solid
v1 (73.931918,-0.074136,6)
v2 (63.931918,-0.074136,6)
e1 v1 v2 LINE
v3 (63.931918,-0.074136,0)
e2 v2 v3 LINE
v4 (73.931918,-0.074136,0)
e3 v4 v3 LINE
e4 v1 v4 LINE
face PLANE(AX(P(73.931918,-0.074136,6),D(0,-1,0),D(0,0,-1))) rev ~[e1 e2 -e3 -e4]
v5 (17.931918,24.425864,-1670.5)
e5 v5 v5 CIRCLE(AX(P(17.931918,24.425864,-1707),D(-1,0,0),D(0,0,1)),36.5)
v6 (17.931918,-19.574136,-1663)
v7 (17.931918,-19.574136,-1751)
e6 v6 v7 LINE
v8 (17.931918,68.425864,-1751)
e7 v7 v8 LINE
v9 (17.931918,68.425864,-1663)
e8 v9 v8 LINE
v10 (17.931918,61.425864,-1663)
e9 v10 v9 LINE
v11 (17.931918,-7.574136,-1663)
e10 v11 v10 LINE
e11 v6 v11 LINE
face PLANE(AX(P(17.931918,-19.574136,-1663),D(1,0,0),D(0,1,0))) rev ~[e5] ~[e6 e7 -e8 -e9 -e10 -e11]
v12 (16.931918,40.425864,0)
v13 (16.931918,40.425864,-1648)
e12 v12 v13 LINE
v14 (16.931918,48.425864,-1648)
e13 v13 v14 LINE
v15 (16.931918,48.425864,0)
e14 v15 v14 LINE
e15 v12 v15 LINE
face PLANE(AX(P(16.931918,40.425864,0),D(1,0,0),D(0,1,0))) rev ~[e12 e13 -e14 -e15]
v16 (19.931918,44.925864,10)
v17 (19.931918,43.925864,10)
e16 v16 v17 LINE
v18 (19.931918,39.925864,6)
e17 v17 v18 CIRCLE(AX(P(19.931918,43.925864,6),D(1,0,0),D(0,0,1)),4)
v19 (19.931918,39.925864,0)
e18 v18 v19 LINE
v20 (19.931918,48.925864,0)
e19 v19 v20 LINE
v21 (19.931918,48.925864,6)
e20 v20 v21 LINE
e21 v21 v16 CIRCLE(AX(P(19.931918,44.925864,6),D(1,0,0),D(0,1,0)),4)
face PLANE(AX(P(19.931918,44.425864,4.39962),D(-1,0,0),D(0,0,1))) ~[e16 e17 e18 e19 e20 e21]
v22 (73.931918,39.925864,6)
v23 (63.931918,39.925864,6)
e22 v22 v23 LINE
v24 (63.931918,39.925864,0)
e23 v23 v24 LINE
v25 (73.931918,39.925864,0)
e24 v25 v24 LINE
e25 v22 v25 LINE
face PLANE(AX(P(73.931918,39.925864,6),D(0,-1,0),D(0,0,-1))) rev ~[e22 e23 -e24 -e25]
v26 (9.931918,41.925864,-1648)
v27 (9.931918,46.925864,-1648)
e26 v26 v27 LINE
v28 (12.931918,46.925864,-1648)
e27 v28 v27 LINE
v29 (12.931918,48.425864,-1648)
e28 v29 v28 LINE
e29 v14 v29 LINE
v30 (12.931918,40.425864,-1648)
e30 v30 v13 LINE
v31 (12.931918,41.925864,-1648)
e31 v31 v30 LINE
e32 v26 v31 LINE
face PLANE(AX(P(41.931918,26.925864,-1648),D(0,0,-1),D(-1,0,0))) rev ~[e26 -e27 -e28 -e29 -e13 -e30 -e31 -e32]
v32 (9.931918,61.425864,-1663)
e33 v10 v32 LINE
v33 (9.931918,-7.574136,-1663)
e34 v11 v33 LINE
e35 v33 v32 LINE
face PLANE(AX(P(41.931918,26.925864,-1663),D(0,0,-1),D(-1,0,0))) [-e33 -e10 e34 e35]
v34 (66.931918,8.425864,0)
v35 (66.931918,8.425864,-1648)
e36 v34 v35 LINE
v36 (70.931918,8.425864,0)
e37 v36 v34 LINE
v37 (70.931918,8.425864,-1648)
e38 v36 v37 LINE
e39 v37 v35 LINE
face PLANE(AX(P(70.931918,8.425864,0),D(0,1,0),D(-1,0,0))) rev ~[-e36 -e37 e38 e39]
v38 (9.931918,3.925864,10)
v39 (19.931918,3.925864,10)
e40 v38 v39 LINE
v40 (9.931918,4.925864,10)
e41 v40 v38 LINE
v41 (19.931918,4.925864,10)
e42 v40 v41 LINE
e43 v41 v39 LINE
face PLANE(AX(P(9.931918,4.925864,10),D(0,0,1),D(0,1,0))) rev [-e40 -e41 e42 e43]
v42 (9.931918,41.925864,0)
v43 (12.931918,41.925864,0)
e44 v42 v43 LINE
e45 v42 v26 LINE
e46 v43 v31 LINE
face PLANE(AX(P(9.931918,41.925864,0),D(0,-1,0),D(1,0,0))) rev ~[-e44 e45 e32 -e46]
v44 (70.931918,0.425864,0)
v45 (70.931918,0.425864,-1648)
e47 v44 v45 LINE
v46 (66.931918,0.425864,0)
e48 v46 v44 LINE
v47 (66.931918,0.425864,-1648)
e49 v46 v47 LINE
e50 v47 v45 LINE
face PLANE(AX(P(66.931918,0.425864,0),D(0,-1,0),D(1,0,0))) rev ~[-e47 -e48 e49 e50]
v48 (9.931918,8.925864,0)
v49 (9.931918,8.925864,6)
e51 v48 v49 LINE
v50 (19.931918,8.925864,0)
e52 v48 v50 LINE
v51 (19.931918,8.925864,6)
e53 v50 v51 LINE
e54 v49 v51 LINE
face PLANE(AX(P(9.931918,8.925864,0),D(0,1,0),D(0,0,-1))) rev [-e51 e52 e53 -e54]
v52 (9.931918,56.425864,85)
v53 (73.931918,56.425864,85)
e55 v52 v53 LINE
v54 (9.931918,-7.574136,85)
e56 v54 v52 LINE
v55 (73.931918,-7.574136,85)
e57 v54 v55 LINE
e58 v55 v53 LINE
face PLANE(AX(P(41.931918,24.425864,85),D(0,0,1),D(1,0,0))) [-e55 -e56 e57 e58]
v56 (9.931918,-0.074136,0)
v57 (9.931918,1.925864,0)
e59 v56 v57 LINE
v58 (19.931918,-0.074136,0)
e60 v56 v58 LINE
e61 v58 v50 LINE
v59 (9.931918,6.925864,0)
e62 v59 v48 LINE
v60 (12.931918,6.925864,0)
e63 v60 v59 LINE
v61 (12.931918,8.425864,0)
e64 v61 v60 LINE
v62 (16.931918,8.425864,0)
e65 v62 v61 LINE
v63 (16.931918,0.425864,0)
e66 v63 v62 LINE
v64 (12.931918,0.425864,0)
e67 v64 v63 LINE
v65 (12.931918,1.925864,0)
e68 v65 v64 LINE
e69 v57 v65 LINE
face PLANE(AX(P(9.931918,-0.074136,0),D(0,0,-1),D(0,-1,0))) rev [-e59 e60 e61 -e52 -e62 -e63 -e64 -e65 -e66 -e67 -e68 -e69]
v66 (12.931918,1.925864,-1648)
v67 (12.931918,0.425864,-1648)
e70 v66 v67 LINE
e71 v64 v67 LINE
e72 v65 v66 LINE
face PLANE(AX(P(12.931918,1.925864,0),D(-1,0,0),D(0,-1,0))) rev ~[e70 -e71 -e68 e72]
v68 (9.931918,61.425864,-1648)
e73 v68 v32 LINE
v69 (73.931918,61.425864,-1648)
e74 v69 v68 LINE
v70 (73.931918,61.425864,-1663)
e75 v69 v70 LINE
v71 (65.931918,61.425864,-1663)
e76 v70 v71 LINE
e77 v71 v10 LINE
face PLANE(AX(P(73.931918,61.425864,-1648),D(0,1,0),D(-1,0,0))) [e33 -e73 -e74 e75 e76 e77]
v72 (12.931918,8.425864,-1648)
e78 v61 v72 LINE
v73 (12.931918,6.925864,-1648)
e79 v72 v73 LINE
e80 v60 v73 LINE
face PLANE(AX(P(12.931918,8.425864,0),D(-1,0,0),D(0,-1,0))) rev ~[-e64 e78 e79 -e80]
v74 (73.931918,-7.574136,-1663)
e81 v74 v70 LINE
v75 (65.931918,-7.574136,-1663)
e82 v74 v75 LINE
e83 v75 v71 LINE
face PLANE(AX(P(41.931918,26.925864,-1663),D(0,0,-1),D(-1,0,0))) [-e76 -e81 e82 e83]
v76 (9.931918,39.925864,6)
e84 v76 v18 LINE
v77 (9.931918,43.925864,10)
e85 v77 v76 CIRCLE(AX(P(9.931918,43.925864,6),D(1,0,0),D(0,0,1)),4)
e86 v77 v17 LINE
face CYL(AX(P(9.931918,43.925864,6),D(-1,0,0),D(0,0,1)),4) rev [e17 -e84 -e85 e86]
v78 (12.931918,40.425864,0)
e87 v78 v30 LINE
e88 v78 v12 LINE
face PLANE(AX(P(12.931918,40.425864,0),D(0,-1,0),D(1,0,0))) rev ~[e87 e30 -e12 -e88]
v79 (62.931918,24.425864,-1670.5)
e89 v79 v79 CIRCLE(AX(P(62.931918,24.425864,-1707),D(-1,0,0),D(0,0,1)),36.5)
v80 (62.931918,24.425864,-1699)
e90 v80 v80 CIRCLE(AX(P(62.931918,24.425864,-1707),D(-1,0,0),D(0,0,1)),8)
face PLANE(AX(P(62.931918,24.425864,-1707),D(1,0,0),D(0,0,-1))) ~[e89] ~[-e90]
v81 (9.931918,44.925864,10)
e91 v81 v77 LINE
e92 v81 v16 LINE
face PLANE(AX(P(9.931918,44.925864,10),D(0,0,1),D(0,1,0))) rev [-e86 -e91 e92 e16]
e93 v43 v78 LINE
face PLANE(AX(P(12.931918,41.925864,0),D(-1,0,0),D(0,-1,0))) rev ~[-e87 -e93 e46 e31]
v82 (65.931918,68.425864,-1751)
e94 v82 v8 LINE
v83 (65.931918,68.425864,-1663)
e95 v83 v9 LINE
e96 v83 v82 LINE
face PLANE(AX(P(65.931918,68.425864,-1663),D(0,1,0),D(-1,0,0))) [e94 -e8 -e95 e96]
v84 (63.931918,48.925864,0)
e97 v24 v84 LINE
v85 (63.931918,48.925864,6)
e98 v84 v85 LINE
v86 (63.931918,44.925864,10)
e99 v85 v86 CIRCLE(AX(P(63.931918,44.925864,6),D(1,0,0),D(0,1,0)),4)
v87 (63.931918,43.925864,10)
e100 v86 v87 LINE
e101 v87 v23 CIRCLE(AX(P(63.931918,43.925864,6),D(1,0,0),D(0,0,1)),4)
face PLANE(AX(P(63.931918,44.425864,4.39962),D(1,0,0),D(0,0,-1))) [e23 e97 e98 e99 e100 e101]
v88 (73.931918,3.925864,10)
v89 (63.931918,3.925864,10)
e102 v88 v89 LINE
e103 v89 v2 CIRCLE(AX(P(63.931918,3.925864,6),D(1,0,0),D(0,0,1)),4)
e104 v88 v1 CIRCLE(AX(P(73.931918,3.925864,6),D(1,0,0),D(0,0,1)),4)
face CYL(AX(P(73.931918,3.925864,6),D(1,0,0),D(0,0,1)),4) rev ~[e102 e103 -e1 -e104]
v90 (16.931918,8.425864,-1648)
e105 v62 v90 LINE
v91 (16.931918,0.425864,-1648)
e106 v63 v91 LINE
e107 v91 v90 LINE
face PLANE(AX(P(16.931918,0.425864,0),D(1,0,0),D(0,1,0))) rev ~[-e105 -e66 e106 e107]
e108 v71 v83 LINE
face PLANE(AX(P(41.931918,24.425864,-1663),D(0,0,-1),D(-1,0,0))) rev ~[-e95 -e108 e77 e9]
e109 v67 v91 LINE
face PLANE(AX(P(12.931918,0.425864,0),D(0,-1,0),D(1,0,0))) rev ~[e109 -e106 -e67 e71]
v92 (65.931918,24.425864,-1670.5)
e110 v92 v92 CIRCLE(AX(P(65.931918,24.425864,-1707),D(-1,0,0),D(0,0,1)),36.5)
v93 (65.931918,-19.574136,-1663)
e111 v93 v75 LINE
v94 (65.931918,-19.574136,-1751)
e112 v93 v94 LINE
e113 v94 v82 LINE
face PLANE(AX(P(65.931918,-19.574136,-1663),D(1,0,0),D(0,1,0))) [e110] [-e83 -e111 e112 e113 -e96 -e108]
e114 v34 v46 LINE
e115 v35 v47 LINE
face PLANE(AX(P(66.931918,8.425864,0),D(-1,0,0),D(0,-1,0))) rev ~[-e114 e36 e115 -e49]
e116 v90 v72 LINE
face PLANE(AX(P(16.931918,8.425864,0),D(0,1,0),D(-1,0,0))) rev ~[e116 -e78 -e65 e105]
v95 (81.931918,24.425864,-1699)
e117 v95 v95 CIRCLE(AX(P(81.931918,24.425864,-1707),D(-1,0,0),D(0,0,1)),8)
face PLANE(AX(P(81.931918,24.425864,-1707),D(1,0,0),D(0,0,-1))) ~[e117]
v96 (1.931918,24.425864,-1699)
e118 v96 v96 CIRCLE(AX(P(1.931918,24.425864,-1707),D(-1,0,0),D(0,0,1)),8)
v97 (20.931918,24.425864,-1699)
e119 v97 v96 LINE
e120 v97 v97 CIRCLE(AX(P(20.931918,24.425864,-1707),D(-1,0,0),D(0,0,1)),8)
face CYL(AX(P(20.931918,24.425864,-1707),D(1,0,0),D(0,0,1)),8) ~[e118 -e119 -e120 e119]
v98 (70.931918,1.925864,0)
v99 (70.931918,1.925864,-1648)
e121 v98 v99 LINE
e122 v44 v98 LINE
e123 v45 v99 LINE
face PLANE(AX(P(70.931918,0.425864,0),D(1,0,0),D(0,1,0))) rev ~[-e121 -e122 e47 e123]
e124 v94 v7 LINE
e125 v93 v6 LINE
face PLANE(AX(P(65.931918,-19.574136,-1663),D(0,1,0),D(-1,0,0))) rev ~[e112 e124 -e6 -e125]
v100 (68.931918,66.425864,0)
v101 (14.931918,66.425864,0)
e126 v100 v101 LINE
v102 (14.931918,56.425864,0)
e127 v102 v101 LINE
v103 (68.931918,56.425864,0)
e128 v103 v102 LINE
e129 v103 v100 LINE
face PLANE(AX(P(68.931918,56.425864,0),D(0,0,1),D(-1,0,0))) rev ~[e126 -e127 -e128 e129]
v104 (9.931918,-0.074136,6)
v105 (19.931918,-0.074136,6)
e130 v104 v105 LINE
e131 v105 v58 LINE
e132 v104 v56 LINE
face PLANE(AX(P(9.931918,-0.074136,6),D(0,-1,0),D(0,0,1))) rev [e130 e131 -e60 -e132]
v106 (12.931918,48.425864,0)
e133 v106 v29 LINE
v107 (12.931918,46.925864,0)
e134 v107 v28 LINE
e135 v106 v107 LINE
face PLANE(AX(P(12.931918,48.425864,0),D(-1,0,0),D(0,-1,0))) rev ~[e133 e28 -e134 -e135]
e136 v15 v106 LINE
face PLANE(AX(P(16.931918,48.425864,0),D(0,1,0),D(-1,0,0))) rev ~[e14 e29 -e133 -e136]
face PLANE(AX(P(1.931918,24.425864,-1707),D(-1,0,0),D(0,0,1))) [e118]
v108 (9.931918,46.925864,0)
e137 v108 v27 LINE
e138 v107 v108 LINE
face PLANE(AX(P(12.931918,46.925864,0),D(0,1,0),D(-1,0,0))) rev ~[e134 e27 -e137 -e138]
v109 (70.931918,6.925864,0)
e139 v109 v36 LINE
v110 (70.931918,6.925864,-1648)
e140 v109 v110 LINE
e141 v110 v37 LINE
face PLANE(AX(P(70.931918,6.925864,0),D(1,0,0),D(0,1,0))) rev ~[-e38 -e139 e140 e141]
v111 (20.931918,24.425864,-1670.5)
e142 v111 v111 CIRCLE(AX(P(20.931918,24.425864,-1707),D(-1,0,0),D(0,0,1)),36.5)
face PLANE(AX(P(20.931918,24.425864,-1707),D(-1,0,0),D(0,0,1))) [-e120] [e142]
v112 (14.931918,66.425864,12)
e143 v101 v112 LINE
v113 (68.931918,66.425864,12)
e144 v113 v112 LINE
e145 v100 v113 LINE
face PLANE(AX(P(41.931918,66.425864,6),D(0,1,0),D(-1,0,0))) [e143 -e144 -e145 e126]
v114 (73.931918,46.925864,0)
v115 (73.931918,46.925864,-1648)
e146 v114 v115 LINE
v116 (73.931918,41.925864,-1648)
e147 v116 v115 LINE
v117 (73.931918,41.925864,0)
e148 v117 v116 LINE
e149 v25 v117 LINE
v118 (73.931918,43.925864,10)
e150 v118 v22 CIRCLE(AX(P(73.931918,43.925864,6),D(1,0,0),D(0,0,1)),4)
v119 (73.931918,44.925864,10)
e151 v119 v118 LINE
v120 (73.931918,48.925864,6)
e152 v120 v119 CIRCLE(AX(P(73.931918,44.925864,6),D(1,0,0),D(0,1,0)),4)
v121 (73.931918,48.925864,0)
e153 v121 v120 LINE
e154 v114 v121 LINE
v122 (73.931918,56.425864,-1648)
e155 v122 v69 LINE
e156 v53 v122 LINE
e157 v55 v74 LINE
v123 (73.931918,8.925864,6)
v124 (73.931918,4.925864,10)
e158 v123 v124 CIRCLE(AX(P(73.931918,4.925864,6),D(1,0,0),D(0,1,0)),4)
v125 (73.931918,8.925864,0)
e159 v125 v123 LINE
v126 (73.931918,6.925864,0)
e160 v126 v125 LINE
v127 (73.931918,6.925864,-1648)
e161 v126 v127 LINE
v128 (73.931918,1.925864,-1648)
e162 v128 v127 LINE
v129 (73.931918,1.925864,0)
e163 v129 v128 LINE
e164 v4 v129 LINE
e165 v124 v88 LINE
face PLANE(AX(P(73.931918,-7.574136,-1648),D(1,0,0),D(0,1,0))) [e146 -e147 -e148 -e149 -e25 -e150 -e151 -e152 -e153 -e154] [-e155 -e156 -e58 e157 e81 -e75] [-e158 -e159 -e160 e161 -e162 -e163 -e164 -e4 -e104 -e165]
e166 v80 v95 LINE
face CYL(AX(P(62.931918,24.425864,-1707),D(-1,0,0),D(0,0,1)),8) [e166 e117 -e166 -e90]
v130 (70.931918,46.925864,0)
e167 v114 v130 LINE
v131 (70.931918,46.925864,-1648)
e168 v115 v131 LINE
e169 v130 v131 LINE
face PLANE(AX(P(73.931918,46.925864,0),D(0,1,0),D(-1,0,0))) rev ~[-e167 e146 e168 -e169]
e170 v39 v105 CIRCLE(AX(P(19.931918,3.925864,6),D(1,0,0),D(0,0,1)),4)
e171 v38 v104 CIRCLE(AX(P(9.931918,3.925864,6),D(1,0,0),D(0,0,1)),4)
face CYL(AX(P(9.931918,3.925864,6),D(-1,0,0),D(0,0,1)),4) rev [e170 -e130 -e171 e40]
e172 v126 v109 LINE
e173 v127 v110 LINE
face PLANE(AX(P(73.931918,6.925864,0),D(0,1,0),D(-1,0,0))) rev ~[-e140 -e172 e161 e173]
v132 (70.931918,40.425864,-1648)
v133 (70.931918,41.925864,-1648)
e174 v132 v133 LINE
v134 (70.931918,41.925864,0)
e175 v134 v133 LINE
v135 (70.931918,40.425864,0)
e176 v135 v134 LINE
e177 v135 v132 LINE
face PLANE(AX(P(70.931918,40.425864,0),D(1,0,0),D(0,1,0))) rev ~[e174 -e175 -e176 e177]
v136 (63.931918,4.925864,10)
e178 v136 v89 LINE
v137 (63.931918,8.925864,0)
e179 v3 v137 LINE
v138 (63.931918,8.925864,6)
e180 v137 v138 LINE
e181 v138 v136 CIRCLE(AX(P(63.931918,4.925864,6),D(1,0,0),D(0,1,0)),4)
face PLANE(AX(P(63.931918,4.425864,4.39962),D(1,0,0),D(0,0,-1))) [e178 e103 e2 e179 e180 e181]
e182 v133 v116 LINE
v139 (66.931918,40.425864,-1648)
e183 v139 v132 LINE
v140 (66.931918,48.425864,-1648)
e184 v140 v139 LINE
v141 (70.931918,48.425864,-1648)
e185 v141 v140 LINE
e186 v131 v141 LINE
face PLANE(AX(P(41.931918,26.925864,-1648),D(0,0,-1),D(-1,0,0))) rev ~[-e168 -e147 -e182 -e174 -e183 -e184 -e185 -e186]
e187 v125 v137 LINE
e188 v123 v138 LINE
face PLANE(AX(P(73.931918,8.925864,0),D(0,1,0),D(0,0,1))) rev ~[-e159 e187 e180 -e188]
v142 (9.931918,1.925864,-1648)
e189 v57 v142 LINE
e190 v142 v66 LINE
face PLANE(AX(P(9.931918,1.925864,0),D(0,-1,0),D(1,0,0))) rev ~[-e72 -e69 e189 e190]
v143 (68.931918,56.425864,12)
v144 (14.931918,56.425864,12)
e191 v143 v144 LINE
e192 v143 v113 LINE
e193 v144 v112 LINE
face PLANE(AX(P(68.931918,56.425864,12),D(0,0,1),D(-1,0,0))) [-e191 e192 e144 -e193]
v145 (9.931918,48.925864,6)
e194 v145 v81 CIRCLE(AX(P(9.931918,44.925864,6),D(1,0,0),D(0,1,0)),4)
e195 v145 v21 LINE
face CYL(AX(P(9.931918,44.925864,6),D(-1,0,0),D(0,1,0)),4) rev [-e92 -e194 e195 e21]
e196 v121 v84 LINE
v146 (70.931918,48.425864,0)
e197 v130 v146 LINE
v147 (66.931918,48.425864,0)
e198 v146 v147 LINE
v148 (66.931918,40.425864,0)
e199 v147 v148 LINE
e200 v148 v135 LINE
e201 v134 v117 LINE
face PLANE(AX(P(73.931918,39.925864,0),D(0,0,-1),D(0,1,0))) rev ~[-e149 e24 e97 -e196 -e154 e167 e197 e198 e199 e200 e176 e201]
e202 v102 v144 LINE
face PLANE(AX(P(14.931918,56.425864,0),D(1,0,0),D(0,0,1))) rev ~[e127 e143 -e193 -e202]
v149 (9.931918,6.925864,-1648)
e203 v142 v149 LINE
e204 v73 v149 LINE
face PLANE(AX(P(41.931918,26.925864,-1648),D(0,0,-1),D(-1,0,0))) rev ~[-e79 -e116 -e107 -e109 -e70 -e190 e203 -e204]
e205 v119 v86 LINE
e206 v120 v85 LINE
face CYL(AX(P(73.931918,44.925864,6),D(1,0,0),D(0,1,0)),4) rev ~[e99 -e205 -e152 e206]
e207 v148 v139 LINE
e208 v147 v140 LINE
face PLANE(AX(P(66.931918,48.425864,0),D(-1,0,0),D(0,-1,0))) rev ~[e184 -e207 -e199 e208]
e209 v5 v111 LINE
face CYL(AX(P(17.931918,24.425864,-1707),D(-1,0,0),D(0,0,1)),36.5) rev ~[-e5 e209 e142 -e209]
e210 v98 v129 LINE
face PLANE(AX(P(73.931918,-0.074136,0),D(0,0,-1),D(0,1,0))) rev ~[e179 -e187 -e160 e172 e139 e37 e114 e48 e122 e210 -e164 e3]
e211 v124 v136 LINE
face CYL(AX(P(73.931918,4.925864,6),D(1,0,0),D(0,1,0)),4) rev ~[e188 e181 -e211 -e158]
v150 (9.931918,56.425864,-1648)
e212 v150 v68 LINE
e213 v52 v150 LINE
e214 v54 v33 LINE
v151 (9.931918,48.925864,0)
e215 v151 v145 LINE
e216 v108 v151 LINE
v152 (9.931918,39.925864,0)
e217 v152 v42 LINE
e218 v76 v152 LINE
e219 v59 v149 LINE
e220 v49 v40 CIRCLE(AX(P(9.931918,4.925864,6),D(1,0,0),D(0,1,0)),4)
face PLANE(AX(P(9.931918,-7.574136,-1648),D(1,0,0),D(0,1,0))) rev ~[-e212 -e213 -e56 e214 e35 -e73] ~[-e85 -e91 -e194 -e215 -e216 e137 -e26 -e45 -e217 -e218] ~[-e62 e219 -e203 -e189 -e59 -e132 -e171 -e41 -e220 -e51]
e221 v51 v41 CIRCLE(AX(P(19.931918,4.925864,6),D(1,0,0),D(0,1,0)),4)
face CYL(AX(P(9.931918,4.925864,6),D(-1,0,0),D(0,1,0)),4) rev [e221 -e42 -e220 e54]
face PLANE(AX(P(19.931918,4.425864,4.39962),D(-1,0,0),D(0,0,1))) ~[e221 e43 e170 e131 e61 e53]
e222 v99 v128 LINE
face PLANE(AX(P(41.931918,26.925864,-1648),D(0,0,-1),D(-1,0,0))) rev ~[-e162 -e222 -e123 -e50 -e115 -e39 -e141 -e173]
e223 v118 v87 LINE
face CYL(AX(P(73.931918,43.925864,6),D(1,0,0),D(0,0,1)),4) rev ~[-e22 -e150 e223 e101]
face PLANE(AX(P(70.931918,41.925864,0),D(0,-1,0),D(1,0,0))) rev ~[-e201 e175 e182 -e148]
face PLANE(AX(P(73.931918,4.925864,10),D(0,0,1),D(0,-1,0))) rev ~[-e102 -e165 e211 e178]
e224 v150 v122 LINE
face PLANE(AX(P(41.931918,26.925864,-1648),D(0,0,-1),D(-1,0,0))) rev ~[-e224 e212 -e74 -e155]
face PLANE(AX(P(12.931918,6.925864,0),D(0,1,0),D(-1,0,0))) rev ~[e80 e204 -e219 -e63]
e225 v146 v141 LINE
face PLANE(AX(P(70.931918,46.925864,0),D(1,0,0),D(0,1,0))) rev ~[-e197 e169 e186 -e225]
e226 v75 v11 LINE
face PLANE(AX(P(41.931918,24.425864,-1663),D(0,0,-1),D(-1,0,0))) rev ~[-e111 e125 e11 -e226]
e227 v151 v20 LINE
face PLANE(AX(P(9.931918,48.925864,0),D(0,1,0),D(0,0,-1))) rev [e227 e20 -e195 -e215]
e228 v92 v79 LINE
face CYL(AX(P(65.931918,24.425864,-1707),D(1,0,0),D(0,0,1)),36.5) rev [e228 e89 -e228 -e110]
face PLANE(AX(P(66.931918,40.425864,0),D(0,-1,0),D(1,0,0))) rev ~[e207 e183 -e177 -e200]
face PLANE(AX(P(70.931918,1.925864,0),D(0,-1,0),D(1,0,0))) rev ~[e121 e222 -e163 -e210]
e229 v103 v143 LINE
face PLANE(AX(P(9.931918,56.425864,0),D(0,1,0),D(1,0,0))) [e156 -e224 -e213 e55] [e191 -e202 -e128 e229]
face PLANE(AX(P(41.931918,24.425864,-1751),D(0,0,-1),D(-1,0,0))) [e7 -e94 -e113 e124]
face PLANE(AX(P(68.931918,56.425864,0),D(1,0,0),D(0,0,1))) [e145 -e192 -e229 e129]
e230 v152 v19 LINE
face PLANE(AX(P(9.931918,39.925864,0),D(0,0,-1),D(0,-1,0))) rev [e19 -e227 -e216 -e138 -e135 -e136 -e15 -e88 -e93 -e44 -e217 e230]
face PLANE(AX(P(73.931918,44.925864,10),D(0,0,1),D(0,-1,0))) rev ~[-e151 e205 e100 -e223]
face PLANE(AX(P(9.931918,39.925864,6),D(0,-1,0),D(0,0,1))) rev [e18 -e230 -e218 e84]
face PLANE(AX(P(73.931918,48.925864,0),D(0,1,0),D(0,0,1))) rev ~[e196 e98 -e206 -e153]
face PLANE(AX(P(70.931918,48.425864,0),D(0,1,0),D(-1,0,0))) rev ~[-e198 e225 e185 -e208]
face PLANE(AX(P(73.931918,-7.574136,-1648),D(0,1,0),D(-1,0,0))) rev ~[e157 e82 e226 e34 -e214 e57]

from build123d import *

# Parameters (mm, degrees)
EXTRUDE_642_DEPTH   = 1648
SKETCH_2_W          = 64
SKETCH_2_H          = 64
EXTRUDE_1_DEPTH     = 85
SKETCH_4_W          = 54
SKETCH_4_H          = 12
EXTRUDE_2_DEPTH     = 10
CUT_EXTRUDE_1_DEPTH = 10
SKETCH_6_W          = 64
SKETCH_6_H          = 69
EXTRUDE_3_DEPTH     = 15
SKETCH_7_W          = 48
SKETCH_7_H          = 88
EXTRUDE_4_DEPTH     = 88
SKETCH_8_R          = 36.5
CUT_EXTRUDE_2_DEPTH = 3
SKETCH_9_R          = 8
EXTRUDE_5_DEPTH     = 19


with BuildPart() as part:
    # 草图1 → Extrude 642 (new body)
    with BuildSketch(Plane.XY):
        Polygon((9.931917842, 6.925864063), (9.931917842, 41.925864063), (12.931917842, 41.925864063), (12.931917842, 40.425864063), (16.931917842, 40.425864063), (16.931917842, 48.425864063), (12.931917842, 48.425864063), (12.931917842, 46.925864063), (9.931917842, 46.925864063), (9.931917842, 56.425864063), (73.931917842, 56.425864063), (73.931917842, 46.925864063), (70.931917842, 46.925864063), (70.931917842, 48.425864063), (66.931917842, 48.425864063), (66.931917842, 40.425864063), (70.931917842, 40.425864063), (70.931917842, 41.925864063), (73.931917842, 41.925864063), (73.931917842, 6.925864063), (70.931917842, 6.925864063), (70.931917842, 8.425864063), (66.931917842, 8.425864063), (66.931917842, 0.425864063), (70.931917842, 0.425864063), (70.931917842, 1.925864063), (73.931917842, 1.925864063), (73.931917842, -7.574135937), (9.931917842, -7.574135937), (9.931917842, 1.925864063), (12.931917842, 1.925864063), (12.931917842, 0.425864063), (16.931917842, 0.425864063), (16.931917842, 8.425864063), (12.931917842, 8.425864063), (12.931917842, 6.925864063), align=None)
    extrude(amount=-EXTRUDE_642_DEPTH)

    # 草图2 → 凸台-拉伸1 (add)
    with BuildSketch(Plane.XY):
        with Locations((41.931917842, 24.425864063)):
            Rectangle(SKETCH_2_W, SKETCH_2_H)
    extrude(amount=EXTRUDE_1_DEPTH)

    # 草图4 → 凸台-拉伸2 (add)
    with BuildSketch(Plane(origin=(0, 56.425864063, 0), x_dir=(-1, 0, 0), z_dir=(0, 1, 0))):
        with Locations((-41.931917842, 6)):
            Rectangle(SKETCH_4_W, SKETCH_4_H)
    extrude(amount=EXTRUDE_2_DEPTH)

    # 草图5 → 切除-拉伸1 (cut)
    with BuildSketch(Plane(origin=(73.931917842, 0, 0), x_dir=(0, 0, -1), z_dir=(1, 0, 0))):
        with BuildLine():
            Line((0, 48.925864063), (-6, 48.925864063))
            ThreePointArc((-6, 48.925864063), (-8.828427125, 47.754291188), (-10, 44.925864063))
            Line((-10, 44.925864063), (-10, 43.925864063))
            ThreePointArc((-10, 43.925864063), (-8.828427125, 41.097436938), (-6, 39.925864063))
            Line((-6, 39.925864063), (0, 39.925864063))
            Line((0, 39.925864063), (0, 48.925864063))
        make_face()
        with BuildLine():
            Line((0, 8.925864063), (-6, 8.925864063))
            ThreePointArc((-6, 8.925864063), (-8.828427125, 7.754291188), (-10, 4.925864063))
            Line((-10, 4.925864063), (-10, 3.925864063))
            ThreePointArc((-10, 3.925864063), (-8.828427125, 1.097436938), (-6, -0.074135937))
            Line((-6, -0.074135937), (0, -0.074135937))
            Line((0, -0.074135937), (0, 8.925864063))
        make_face()
    cut_extrude_1 = extrude(amount=-CUT_EXTRUDE_1_DEPTH, mode=Mode.SUBTRACT)

    # 镜向1: 切除-拉伸1 across plane
    add(cut_extrude_1.mirror(Plane.ZY.offset(-41.931917842)), mode=Mode.SUBTRACT)

    # 草图6 → 凸台-拉伸3 (add)
    with BuildSketch(Plane(origin=(0, 0, -1648), x_dir=(-1, 0, 0), z_dir=(0, 0, -1))):
        with Locations((-41.931917842, 26.925864063)):
            Rectangle(SKETCH_6_W, SKETCH_6_H)
    extrude(amount=EXTRUDE_3_DEPTH)

    # 草图7 → 凸台-拉伸4 (add)
    with BuildSketch(Plane(origin=(0, 0, -1663), x_dir=(-1, 0, 0), z_dir=(0, 0, -1))):
        with Locations((-41.931917842, 24.425864063)):
            Rectangle(SKETCH_7_W, SKETCH_7_H)
    extrude(amount=EXTRUDE_4_DEPTH)

    # 草图8 → 切除-拉伸2 (cut)
    with BuildSketch(Plane.ZY.offset(-17.931917842)):
        with Locations((-1707, 24.425864063)):
            Circle(SKETCH_8_R)
    cut_extrude_2 = extrude(amount=-CUT_EXTRUDE_2_DEPTH, mode=Mode.SUBTRACT)

    # 草图9 → 凸台-拉伸5 (add)
    with BuildSketch(Plane.ZY.offset(-20.931917842)):
        with Locations((-1707, 24.425864063)):
            Circle(SKETCH_9_R)
    extrude_5 = extrude(amount=EXTRUDE_5_DEPTH)

    # 镜向2: 切除-拉伸2, 凸台-拉伸5 across plane
    add(cut_extrude_2.mirror(Plane.ZY.offset(-41.931917842)), mode=Mode.SUBTRACT)
    add(extrude_5.mirror(Plane.ZY.offset(-41.931917842)))


solid = part.part
